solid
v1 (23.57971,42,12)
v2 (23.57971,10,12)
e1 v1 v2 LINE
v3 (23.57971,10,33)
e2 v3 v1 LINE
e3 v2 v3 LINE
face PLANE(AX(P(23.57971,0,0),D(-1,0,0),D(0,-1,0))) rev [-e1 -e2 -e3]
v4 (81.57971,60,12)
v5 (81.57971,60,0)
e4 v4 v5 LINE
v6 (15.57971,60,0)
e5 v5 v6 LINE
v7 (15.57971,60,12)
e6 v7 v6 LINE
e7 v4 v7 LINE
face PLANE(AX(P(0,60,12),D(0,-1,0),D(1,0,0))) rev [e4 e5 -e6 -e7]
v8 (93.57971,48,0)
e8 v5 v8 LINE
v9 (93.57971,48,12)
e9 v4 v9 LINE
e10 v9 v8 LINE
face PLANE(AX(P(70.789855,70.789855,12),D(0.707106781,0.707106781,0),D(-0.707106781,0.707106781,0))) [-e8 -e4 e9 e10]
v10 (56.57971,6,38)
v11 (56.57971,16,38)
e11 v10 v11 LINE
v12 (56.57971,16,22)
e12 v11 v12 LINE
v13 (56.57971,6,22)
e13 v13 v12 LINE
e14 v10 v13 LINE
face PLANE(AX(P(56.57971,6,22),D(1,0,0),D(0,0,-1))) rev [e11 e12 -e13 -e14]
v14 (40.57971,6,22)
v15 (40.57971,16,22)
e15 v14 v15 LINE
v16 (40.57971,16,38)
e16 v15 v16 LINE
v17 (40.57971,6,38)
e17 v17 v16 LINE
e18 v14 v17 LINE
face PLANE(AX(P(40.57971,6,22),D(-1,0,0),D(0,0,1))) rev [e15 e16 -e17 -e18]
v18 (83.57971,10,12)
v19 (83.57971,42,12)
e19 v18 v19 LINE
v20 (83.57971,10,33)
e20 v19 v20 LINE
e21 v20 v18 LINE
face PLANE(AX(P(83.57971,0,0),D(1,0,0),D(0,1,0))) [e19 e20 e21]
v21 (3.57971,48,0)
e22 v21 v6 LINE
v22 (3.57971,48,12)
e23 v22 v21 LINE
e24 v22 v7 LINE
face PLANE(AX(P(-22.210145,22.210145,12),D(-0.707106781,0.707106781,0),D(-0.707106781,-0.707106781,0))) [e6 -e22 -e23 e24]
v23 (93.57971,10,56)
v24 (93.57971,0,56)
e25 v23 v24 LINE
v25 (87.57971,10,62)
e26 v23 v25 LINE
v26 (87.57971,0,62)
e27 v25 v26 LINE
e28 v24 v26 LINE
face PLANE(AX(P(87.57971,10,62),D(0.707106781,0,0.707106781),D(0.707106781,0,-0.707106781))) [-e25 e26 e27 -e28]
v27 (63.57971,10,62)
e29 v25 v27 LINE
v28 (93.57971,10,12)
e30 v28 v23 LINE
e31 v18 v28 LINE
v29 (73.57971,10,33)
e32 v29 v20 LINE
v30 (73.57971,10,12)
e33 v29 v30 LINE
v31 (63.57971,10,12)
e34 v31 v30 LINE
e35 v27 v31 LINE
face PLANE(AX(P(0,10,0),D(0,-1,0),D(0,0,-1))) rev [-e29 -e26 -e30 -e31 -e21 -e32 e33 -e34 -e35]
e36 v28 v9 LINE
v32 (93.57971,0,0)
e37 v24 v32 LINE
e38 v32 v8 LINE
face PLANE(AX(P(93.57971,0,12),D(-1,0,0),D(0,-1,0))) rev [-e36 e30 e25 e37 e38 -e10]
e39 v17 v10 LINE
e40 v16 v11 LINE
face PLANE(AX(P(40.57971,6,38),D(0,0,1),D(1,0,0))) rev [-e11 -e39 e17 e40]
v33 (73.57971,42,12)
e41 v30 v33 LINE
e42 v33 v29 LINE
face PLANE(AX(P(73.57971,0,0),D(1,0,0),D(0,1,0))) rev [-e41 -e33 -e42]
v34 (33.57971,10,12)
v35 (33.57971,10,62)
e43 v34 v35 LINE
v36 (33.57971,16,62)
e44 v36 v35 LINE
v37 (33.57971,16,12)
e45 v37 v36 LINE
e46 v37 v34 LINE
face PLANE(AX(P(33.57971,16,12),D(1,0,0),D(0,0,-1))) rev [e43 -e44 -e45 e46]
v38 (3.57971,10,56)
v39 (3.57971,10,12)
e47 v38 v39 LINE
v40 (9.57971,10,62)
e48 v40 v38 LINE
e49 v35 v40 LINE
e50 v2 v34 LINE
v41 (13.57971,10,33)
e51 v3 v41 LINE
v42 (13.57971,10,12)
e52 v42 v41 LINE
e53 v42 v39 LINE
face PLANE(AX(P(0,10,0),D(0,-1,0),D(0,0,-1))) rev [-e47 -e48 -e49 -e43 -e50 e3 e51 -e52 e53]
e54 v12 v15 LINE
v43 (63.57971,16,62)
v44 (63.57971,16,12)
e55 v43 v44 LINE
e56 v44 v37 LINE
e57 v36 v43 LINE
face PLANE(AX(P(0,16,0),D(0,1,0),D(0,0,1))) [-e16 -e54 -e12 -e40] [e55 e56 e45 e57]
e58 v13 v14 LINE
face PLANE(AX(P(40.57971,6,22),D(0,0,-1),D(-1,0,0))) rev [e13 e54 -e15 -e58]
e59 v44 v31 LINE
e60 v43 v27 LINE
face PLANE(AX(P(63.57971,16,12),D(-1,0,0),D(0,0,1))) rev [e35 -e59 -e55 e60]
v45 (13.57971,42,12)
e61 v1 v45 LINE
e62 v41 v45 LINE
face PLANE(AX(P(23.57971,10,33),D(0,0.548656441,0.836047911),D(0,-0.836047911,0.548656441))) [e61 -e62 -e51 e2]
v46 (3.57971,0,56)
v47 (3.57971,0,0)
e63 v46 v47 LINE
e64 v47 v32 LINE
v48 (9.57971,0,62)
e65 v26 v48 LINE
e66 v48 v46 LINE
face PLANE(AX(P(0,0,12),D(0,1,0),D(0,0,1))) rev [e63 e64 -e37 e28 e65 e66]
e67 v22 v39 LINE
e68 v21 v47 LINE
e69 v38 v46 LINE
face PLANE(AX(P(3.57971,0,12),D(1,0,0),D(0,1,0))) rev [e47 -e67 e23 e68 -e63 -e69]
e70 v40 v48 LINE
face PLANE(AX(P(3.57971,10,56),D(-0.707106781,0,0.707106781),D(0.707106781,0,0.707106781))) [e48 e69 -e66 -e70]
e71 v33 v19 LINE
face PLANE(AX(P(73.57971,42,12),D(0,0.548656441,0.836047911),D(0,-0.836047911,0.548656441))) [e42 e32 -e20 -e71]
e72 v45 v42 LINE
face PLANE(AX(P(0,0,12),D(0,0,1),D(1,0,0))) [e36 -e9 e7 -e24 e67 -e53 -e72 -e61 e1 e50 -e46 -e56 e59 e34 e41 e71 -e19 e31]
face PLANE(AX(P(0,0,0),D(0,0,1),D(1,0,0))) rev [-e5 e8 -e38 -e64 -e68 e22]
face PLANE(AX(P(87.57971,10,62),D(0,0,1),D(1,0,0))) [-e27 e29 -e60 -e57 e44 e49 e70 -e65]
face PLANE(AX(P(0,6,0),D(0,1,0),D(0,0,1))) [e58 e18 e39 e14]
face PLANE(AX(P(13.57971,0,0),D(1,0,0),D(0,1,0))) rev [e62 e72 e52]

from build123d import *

# Parameters (mm, degrees)
BRACKET_BODY_DEPTH          = 12
CHAMFERED_PLATE_78X44_DEPTH = 10
CENTRE_PAD_SKETCH_W         = 30
CENTRE_PAD_SKETCH_H         = 50
CENTRE_PAD_30X30_DEPTH      = 6
PAD_POCKET_SKETCH_W         = 16
PAD_POCKET_SKETCH_H         = 16
PAD_POCKET_10X7_DEPTH       = 10
GUSSET_RIB_1_DEPTH          = 20
GUSSET_RIB_1_TRIM_DEPTH     = 10
GUSSET_RIB_2_DEPTH          = 20
GUSSET_RIB_2_TRIM_DEPTH     = 10


with BuildPart() as part:
    # Bracket Profile Sketch → Bracket Body (new body)
    with BuildSketch(Plane.XY):
        Polygon((3.579710145, 48), (3.579710145, 0), (93.579710145, 0), (93.579710145, 48), (81.579710145, 60), (15.579710145, 60), align=None)
    extrude(amount=BRACKET_BODY_DEPTH)

    # Chamfered Plate Sketch → Chamfered Plate 78x44 (add)
    with BuildSketch(Plane.XZ):
        Polygon((3.579710145, 12), (3.579710145, 56), (9.579710145, 62), (87.579710145, 62), (93.579710145, 56), (93.579710145, 12), align=None)
    extrude(amount=-CHAMFERED_PLATE_78X44_DEPTH)

    # Centre Pad Sketch → Centre Pad 30x30 (add)
    with BuildSketch(Plane(origin=(0, 10, 0), x_dir=(1, 0, 0), z_dir=(0, 1, 0))):
        with Locations((48.579710145, -37)):
            Rectangle(CENTRE_PAD_SKETCH_W, CENTRE_PAD_SKETCH_H)
    extrude(amount=CENTRE_PAD_30X30_DEPTH)

    # Pad Pocket Sketch → Pad Pocket 10x7 (cut)
    with BuildSketch(Plane(origin=(0, 16, 0), x_dir=(1, 0, 0), z_dir=(0, 1, 0))):
        with Locations((48.579710145, -30)):
            Rectangle(PAD_POCKET_SKETCH_W, PAD_POCKET_SKETCH_H)
    extrude(amount=-PAD_POCKET_10X7_DEPTH, mode=Mode.SUBTRACT)

    # Rib 1 Sketch → Gusset Rib 1 (add)
    with BuildSketch(Plane.ZY.offset(-3.579710145)):
        Polygon((12, 10), (12, 42), (33, 10), align=None)
    extrude(amount=-GUSSET_RIB_1_DEPTH)

    # Rib 1 Trim Sketch → Gusset Rib 1 Trim (cut)
    with BuildSketch(Plane.ZY.offset(-3.579710145)):
        Polygon((12, 42), (12, 10), (33, 10), align=None)
    extrude(amount=-GUSSET_RIB_1_TRIM_DEPTH, mode=Mode.SUBTRACT)

    # Rib 2 Sketch → Gusset Rib 2 (add)
    with BuildSketch(Plane(origin=(93.579710145, 0, 0), x_dir=(0, 0, -1), z_dir=(1, 0, 0))):
        Polygon((-12, 10), (-12, 42), (-33, 10), align=None)
    extrude(amount=-GUSSET_RIB_2_DEPTH)

    # Rib 2 Trim Sketch → Gusset Rib 2 Trim (cut)
    with BuildSketch(Plane(origin=(93.579710145, 0, 0), x_dir=(0, 0, -1), z_dir=(1, 0, 0))):
        Polygon((-12, 42), (-12, 10), (-33, 10), align=None)
    extrude(amount=-GUSSET_RIB_2_TRIM_DEPTH, mode=Mode.SUBTRACT)


solid = part.part
